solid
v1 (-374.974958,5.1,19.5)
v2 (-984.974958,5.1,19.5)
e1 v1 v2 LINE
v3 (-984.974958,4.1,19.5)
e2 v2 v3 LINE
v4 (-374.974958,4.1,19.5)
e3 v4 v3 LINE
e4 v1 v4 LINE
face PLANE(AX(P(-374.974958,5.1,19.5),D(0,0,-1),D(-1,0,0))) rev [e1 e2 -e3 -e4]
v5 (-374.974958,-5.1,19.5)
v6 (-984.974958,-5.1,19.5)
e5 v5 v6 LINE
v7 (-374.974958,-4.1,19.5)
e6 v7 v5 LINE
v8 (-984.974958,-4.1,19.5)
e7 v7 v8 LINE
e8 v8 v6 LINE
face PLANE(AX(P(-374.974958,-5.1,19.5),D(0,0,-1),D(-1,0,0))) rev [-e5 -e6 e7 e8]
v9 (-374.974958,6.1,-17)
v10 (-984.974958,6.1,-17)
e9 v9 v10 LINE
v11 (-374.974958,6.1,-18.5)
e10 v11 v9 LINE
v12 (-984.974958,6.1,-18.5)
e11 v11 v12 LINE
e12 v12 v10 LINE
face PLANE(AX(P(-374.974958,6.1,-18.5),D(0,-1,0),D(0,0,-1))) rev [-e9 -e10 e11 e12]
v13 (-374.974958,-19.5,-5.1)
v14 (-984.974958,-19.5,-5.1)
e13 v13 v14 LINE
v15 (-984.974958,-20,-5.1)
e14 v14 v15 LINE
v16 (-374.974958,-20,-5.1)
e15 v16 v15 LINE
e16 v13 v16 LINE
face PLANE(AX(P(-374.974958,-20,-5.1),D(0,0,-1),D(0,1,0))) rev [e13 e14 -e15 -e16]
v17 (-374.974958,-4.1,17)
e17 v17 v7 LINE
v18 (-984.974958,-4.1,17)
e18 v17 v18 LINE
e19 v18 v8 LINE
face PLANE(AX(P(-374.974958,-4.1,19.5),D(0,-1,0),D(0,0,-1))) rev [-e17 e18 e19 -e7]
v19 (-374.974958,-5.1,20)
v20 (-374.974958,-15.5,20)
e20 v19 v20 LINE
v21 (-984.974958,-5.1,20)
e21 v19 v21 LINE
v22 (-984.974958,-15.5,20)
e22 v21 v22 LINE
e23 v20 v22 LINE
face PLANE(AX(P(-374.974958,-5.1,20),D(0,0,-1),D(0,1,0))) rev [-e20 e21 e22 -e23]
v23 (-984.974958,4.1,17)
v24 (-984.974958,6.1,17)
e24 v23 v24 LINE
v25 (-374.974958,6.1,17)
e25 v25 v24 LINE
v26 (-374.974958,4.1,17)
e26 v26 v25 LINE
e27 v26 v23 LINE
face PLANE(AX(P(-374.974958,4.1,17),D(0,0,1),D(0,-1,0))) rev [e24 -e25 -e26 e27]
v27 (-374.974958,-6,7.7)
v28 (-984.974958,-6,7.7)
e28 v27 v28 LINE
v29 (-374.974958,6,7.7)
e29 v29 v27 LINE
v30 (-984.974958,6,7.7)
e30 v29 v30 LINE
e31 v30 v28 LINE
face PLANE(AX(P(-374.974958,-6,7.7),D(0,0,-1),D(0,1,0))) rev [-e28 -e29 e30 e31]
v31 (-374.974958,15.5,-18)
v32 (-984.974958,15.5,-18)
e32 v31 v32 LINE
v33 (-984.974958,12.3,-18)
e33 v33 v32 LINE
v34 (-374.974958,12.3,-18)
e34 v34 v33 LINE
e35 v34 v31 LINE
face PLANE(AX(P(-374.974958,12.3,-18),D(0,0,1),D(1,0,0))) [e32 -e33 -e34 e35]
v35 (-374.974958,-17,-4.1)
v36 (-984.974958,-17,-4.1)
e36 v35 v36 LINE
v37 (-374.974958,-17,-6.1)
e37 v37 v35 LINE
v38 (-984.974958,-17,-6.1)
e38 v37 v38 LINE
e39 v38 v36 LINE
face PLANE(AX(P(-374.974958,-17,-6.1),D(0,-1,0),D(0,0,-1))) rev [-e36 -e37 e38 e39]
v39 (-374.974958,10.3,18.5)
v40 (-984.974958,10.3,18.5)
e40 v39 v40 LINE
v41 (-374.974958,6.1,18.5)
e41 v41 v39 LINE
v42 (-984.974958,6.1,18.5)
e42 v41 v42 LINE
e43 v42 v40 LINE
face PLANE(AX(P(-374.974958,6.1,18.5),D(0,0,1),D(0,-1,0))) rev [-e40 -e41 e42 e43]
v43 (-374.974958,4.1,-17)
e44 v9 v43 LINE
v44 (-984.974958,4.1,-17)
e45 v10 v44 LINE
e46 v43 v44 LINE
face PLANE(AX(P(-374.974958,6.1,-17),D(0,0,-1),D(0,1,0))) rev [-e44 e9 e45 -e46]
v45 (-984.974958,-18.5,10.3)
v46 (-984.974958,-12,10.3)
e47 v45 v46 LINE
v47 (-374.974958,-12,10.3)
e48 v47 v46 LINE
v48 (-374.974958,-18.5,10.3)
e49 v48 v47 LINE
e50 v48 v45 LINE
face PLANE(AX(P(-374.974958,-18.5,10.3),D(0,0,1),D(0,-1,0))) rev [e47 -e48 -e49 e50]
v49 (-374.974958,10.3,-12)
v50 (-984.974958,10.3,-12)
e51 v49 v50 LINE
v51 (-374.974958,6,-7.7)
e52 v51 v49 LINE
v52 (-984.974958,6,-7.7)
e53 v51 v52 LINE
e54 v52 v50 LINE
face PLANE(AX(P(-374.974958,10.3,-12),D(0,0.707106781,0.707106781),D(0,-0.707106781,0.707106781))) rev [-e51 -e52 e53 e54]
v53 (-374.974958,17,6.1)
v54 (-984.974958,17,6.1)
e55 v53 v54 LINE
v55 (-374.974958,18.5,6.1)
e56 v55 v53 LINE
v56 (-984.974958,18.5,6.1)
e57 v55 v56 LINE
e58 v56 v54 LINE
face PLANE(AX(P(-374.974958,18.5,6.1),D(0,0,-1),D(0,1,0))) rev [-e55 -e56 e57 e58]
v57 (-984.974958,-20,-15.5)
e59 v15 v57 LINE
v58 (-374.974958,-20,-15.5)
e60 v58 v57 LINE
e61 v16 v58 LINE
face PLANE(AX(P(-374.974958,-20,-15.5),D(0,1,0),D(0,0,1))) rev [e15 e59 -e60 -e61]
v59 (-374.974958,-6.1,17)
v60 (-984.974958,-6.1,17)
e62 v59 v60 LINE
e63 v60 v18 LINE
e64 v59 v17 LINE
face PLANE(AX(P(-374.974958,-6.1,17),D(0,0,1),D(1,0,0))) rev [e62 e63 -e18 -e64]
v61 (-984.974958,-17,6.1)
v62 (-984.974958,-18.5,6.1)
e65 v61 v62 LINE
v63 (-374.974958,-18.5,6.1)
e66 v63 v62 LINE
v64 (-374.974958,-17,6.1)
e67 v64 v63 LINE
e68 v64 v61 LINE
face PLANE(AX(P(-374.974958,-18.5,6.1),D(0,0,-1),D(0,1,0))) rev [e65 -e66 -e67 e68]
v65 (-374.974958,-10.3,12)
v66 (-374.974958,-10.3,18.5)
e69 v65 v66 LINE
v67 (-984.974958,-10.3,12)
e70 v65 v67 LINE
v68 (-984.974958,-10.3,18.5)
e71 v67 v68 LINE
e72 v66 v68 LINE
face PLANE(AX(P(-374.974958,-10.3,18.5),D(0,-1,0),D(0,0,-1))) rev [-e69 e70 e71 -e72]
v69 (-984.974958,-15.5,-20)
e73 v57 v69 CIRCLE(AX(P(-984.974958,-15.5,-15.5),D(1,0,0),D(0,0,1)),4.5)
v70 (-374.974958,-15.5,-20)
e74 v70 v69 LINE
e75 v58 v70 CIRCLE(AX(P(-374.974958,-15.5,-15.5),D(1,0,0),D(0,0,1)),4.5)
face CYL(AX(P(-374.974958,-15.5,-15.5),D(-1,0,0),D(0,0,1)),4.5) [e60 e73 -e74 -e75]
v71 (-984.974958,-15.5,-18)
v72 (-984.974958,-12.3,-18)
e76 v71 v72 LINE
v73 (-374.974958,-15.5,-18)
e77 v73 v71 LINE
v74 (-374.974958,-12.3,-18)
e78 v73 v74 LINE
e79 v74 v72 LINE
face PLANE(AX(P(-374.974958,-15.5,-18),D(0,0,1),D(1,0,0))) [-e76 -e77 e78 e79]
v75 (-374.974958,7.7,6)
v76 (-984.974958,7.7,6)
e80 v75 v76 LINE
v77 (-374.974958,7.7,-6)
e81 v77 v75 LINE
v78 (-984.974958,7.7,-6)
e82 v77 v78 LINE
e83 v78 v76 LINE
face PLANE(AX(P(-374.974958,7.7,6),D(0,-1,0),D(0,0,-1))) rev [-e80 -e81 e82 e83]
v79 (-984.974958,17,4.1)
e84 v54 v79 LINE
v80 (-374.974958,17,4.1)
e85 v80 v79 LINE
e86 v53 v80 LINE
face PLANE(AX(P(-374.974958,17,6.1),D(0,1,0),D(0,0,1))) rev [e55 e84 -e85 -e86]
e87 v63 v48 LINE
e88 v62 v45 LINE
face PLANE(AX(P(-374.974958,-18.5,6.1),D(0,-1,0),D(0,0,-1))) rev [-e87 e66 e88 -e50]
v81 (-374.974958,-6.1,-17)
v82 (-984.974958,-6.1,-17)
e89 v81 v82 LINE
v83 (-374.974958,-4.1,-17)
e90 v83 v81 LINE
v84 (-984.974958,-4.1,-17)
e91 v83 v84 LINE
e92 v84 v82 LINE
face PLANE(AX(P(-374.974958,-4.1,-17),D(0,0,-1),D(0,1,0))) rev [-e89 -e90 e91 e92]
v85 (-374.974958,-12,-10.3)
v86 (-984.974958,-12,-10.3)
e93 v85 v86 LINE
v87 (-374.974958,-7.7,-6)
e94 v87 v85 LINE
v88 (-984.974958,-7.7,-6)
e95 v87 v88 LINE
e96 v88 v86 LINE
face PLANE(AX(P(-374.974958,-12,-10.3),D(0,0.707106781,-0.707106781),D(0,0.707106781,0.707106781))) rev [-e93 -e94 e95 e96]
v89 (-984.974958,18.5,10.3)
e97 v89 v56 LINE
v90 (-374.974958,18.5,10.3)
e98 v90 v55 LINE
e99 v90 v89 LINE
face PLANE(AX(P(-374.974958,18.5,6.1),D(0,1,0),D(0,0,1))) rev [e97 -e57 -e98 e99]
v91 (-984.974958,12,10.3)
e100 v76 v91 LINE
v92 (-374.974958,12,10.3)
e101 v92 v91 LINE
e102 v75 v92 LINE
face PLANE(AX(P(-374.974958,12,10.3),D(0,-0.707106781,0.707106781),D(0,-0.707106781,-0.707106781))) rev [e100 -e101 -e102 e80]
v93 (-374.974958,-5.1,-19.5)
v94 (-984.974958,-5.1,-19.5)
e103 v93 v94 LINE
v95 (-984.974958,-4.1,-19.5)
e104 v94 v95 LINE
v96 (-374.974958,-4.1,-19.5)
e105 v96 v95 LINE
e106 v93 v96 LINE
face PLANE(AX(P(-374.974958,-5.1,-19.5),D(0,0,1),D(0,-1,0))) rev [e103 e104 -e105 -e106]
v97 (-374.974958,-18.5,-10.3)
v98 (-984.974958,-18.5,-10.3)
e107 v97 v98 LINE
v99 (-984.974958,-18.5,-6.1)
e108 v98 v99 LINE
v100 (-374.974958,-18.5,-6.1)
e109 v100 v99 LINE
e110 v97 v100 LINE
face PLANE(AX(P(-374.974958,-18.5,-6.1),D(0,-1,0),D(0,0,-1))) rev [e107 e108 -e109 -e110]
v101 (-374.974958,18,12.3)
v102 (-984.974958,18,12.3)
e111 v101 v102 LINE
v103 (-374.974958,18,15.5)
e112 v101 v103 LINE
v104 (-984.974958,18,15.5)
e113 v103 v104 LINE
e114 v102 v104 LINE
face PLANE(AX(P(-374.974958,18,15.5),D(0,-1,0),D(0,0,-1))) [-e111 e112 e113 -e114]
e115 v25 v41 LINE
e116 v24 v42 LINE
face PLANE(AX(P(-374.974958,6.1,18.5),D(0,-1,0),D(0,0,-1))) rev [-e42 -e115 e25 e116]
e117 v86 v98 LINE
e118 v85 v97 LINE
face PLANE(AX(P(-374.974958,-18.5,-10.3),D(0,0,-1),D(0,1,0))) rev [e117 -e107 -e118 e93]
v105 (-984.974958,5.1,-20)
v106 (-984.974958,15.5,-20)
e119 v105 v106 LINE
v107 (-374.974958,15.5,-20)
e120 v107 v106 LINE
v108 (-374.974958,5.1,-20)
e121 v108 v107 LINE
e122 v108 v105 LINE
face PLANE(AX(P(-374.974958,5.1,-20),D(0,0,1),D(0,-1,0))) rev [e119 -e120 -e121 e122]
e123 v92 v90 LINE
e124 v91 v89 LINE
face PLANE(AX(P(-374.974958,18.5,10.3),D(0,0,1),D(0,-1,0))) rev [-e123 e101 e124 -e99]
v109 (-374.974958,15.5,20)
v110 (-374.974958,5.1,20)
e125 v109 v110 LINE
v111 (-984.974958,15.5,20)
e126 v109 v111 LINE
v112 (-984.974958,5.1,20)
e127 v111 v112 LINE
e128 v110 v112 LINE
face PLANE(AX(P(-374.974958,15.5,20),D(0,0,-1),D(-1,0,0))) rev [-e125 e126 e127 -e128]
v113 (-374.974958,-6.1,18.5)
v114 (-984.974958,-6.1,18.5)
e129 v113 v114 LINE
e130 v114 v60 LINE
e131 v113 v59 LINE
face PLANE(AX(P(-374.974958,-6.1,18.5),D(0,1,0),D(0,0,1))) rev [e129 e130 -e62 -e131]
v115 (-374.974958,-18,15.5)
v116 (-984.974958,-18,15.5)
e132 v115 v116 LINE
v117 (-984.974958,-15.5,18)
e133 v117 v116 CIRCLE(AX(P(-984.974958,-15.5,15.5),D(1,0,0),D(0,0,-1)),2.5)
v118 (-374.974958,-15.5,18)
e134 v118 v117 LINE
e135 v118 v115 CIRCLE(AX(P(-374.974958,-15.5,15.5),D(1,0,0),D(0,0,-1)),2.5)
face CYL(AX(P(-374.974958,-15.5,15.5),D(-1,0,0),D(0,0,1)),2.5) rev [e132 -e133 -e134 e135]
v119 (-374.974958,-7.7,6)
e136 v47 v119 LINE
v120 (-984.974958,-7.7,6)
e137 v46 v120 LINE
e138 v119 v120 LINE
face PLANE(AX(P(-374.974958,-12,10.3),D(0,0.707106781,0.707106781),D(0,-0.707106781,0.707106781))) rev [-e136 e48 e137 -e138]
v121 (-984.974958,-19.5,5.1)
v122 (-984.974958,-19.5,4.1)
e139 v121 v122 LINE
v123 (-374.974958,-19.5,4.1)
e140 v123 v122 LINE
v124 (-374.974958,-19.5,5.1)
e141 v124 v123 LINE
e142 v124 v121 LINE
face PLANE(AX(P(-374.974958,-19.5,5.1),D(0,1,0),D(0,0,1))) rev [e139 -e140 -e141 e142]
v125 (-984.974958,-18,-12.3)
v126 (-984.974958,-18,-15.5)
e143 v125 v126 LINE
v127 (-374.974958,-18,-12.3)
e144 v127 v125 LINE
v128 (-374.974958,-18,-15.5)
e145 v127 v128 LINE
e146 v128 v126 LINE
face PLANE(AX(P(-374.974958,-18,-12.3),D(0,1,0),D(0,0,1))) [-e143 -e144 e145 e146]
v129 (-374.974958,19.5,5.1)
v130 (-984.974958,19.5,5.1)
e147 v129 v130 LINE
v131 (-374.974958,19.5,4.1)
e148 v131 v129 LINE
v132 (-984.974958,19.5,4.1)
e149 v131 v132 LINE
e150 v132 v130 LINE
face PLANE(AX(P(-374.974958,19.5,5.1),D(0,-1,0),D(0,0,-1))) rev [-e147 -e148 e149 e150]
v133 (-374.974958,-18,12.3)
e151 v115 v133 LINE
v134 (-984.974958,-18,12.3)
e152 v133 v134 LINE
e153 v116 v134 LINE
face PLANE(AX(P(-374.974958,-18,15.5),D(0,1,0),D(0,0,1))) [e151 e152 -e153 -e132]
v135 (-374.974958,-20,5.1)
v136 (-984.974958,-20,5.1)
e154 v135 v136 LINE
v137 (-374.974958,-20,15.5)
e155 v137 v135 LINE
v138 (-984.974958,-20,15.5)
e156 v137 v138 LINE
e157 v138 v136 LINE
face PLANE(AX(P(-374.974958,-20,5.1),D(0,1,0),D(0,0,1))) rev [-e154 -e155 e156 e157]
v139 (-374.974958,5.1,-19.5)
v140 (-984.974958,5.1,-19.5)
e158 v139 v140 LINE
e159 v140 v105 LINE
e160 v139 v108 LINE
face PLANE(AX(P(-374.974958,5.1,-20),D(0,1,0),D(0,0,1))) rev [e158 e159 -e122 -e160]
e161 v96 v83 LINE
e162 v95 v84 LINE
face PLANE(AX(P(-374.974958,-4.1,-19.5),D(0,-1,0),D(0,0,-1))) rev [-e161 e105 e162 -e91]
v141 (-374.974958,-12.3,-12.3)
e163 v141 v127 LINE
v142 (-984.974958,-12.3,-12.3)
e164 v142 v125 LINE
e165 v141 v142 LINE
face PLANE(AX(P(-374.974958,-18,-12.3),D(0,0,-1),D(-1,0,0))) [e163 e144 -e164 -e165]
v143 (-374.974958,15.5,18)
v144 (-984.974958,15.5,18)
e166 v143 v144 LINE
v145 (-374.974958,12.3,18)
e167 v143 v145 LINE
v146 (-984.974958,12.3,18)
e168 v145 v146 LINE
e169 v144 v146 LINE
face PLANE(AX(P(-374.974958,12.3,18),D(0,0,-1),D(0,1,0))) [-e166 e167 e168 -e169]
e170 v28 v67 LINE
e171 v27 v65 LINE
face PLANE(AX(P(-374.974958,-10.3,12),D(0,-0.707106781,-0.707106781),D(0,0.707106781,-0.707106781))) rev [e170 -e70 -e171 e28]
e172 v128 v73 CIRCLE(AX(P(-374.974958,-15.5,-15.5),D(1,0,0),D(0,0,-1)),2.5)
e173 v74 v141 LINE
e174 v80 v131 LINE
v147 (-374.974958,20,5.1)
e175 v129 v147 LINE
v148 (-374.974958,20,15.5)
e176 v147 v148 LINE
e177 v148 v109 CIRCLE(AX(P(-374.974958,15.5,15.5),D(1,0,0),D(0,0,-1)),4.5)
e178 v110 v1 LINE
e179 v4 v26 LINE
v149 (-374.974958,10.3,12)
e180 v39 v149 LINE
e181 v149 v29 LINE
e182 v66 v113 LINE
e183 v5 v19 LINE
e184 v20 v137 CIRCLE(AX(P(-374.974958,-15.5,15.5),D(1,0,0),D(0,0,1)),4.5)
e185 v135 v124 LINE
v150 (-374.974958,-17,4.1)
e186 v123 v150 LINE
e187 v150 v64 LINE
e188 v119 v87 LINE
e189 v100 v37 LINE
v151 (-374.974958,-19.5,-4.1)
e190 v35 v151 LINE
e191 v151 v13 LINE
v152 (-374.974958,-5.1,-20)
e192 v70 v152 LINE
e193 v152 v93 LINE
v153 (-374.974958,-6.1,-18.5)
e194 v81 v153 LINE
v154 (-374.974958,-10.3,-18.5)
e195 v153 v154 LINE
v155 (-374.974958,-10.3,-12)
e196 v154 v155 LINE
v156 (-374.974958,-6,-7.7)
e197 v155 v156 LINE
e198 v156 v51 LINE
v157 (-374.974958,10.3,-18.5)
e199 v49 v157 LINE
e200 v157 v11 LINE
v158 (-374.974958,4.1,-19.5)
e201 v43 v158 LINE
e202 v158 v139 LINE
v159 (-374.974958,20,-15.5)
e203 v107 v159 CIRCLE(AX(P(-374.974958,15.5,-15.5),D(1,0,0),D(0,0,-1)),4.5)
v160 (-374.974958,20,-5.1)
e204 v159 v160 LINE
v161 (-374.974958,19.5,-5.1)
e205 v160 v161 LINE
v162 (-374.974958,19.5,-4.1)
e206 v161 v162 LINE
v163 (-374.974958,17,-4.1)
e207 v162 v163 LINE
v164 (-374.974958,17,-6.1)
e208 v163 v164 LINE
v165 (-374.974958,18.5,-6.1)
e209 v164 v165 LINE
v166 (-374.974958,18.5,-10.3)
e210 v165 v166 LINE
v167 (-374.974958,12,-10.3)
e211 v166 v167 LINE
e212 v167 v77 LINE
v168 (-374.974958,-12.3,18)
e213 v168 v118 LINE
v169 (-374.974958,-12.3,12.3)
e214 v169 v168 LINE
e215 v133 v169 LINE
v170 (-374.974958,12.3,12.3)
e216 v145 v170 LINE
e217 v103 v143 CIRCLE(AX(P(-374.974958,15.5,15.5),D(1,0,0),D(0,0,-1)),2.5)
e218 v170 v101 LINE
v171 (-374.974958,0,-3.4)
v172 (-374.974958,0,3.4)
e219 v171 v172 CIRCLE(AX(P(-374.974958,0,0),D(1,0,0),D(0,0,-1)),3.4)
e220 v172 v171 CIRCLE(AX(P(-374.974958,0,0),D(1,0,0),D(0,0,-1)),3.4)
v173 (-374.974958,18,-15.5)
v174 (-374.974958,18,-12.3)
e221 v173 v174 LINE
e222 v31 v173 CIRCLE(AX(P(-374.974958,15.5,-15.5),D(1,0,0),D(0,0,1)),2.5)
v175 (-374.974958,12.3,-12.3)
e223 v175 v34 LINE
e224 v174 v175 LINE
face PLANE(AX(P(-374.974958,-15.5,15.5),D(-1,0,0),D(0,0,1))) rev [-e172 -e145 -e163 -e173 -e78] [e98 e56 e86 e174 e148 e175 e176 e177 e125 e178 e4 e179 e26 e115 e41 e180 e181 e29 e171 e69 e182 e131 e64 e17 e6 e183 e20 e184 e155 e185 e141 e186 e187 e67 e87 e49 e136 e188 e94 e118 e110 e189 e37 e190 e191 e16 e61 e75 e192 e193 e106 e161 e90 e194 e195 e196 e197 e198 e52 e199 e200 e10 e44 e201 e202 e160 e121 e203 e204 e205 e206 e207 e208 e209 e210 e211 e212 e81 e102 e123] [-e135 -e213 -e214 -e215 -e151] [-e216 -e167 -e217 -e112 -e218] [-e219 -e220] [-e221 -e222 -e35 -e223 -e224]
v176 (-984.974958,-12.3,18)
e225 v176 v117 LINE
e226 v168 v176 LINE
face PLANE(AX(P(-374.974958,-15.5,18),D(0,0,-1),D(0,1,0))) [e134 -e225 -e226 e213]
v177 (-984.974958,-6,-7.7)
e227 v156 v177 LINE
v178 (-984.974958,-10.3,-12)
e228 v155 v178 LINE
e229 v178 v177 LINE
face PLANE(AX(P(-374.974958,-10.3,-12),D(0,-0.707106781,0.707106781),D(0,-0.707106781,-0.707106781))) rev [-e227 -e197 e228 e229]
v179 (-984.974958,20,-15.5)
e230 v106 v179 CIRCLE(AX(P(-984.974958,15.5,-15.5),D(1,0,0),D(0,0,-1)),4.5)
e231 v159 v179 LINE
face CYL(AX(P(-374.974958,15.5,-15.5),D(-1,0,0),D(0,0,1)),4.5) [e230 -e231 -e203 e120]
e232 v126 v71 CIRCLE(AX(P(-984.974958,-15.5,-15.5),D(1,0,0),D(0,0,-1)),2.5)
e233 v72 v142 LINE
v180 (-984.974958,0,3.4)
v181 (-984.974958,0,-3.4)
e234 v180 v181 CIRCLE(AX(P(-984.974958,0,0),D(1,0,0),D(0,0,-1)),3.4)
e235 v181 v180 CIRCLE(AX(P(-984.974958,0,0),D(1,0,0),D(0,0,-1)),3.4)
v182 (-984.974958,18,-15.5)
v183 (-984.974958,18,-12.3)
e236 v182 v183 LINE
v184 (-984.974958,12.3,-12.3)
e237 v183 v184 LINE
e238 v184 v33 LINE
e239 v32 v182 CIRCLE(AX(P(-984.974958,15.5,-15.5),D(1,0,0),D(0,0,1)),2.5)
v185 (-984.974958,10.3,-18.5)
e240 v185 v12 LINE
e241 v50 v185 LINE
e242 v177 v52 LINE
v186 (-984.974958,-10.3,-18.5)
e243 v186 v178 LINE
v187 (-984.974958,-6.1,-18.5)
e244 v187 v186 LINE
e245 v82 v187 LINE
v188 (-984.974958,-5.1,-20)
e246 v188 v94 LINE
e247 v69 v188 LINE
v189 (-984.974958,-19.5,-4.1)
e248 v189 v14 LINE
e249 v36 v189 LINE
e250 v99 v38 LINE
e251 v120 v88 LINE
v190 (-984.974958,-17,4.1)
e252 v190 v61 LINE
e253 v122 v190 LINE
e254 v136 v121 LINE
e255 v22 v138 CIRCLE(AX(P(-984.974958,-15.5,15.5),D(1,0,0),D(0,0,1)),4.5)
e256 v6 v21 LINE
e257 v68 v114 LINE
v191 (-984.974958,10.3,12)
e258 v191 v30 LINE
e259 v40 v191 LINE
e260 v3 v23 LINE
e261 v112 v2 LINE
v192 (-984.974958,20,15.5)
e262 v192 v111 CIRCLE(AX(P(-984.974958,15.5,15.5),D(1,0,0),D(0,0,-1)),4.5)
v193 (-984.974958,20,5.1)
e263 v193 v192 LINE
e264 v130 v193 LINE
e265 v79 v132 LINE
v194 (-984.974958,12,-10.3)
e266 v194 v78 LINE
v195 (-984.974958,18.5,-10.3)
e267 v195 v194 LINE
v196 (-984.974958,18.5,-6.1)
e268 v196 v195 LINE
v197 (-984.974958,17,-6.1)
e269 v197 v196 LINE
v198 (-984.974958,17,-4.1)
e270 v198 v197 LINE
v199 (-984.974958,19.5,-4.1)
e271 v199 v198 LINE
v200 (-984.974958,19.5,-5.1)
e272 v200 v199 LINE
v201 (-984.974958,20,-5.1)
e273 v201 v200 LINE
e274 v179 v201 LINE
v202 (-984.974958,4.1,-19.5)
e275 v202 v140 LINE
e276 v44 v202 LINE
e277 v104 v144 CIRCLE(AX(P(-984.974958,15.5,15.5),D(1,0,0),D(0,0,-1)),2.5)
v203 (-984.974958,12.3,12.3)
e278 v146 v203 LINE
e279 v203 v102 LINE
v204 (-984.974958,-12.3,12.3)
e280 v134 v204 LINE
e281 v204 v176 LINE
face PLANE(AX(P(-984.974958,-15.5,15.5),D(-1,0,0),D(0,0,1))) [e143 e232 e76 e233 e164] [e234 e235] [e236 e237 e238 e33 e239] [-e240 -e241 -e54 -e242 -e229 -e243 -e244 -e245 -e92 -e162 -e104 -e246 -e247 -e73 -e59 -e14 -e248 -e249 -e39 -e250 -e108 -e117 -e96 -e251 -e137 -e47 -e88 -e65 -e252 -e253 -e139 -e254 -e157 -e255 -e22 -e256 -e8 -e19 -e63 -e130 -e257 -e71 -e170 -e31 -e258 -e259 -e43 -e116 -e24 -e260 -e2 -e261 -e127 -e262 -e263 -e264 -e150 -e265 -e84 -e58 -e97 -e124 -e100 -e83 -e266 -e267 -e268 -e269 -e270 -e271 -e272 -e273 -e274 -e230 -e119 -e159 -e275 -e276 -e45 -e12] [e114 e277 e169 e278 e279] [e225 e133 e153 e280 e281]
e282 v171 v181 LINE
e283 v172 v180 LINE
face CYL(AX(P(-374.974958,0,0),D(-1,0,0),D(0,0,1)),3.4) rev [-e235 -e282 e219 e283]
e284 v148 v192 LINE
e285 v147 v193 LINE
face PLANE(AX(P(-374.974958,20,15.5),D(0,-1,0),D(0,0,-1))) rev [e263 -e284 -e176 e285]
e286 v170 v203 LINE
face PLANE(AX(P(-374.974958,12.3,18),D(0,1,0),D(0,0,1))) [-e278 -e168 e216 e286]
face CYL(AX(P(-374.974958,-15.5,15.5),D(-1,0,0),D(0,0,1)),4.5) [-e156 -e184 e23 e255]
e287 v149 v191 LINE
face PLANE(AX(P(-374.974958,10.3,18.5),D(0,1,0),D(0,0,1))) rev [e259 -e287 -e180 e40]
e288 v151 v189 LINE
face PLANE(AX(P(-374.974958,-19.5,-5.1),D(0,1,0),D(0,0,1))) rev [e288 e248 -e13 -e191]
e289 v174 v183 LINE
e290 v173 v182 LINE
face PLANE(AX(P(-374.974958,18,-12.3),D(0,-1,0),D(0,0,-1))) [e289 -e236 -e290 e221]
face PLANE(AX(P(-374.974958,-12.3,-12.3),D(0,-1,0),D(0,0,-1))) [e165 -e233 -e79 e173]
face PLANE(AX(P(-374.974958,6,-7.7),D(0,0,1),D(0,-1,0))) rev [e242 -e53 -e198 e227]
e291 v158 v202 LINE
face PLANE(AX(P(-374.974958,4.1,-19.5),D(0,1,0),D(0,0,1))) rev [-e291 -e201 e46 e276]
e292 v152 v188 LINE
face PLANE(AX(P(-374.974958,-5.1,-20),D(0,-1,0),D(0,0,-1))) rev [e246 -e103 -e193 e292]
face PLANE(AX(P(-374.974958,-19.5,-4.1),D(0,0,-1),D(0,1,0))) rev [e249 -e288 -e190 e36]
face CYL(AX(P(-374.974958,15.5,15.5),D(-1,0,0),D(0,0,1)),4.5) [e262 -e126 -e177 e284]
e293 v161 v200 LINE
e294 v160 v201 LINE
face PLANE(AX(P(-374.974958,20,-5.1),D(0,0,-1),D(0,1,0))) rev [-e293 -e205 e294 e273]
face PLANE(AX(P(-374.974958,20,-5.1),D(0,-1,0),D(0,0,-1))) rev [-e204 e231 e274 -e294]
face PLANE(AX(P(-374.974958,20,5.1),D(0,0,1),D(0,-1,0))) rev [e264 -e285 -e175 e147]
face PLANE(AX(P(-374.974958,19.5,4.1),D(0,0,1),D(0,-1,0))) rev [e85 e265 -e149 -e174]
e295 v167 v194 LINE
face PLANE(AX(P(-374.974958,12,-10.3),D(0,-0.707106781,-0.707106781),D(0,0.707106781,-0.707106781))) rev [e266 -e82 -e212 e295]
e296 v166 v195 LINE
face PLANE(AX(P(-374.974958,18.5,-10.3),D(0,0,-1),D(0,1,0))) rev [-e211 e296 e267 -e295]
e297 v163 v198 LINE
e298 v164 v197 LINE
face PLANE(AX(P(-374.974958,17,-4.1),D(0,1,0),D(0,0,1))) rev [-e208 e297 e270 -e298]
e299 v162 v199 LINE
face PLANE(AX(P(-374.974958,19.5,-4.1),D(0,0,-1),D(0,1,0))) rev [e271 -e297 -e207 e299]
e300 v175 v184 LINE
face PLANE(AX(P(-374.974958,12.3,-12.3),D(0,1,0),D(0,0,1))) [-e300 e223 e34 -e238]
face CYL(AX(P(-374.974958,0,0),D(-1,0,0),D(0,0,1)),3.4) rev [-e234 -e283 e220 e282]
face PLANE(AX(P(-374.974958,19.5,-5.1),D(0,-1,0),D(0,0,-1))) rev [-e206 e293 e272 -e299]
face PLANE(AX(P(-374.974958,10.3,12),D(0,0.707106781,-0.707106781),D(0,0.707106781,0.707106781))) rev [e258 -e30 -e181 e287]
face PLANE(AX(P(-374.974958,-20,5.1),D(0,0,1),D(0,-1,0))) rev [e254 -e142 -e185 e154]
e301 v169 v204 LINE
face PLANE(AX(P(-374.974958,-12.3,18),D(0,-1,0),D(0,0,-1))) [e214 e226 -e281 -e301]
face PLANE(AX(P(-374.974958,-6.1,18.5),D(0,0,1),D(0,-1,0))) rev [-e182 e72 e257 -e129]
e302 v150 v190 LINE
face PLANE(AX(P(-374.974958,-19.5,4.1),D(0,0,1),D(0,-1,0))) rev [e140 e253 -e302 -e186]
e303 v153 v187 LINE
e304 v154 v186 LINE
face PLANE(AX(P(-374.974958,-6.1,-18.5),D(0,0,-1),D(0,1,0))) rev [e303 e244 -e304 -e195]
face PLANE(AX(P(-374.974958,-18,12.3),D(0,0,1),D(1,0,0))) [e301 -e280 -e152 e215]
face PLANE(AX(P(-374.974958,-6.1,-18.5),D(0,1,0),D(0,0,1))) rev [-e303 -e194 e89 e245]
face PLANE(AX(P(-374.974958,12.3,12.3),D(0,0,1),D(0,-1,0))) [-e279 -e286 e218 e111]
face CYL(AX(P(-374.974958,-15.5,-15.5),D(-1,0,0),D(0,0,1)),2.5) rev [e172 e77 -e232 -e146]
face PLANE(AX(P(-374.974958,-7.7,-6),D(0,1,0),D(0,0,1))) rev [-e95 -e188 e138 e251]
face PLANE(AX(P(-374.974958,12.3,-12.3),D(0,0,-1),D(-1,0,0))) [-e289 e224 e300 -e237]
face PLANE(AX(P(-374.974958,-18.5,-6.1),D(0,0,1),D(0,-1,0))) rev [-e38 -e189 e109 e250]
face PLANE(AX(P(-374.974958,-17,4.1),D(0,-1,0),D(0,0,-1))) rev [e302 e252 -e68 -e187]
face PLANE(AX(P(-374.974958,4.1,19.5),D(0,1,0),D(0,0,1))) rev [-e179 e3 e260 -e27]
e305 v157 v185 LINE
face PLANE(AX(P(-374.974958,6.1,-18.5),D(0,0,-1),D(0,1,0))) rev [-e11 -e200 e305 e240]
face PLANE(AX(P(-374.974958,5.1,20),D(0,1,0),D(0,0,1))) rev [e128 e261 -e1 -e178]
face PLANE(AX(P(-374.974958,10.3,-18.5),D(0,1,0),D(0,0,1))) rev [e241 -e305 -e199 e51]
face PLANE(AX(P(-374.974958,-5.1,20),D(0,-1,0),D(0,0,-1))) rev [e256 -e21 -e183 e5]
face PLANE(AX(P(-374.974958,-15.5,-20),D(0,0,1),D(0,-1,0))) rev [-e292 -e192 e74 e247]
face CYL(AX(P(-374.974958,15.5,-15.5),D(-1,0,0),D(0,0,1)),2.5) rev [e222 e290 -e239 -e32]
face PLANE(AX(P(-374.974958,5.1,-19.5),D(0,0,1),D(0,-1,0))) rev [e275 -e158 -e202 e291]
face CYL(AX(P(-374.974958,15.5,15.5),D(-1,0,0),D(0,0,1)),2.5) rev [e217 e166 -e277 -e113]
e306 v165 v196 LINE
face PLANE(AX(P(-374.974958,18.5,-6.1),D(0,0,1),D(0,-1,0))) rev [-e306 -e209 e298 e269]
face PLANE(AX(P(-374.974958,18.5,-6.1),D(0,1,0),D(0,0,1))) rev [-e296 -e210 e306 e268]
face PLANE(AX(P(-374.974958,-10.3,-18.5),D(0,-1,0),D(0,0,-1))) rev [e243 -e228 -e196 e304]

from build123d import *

# Parameters (mm, degrees)
SKETCH1_R                                 = 3.4
ALUMINIUM_PROFILE_40_X_40B_X_R4_5_1_DEPTH = 610


with BuildPart() as part:
    # Sketch1 → Aluminium profile 40 X 40B X R4.5(1) (new body)
    with BuildSketch(Plane.YZ.offset(-984.974958264)):
        with BuildLine():
            Line((-5.1, 20), (-5.1, 19.5))
            Line((-5.1, 19.5), (-4.1, 19.5))
            Line((-4.1, 19.5), (-4.1, 17))
            Line((-4.1, 17), (-6.1, 17))
            Line((-6.1, 17), (-6.1, 18.5))
            Line((-6.1, 18.5), (-10.3, 18.5))
            Line((-10.3, 18.5), (-10.3, 12))
            Line((-10.3, 12), (-6, 7.7))
            Line((-6, 7.7), (6, 7.7))
            Line((6, 7.7), (10.3, 12))
            Line((10.3, 12), (10.3, 18.5))
            Line((10.3, 18.5), (6.1, 18.5))
            Line((6.1, 18.5), (6.1, 17))
            Line((6.1, 17), (4.1, 17))
            Line((4.1, 17), (4.1, 19.5))
            Line((4.1, 19.5), (5.1, 19.5))
            Line((5.1, 19.5), (5.1, 20))
            Line((5.1, 20), (15.5, 20))
            ThreePointArc((15.5, 20), (18.681980515, 18.681980515), (20, 15.5))
            Line((20, 15.5), (20, 5.1))
            Line((20, 5.1), (19.5, 5.1))
            Line((19.5, 5.1), (19.5, 4.1))
            Line((19.5, 4.1), (17, 4.1))
            Line((17, 4.1), (17, 6.1))
            Line((17, 6.1), (18.5, 6.1))
            Line((18.5, 6.1), (18.5, 10.3))
            Line((18.5, 10.3), (12, 10.3))
            Line((12, 10.3), (7.7, 6))
            Line((7.7, 6), (7.7, -6))
            Line((7.7, -6), (12, -10.3))
            Line((12, -10.3), (18.5, -10.3))
            Line((18.5, -10.3), (18.5, -6.1))
            Line((18.5, -6.1), (17, -6.1))
            Line((17, -6.1), (17, -4.1))
            Line((17, -4.1), (19.5, -4.1))
            Line((19.5, -4.1), (19.5, -5.1))
            Line((19.5, -5.1), (20, -5.1))
            Line((20, -5.1), (20, -15.5))
            ThreePointArc((20, -15.5), (18.681980515, -18.681980515), (15.5, -20))
            Line((15.5, -20), (5.1, -20))
            Line((5.1, -20), (5.1, -19.5))
            Line((5.1, -19.5), (4.1, -19.5))
            Line((4.1, -19.5), (4.1, -17))
            Line((4.1, -17), (6.1, -17))
            Line((6.1, -17), (6.1, -18.5))
            Line((6.1, -18.5), (10.3, -18.5))
            Line((10.3, -18.5), (10.3, -12))
            Line((10.3, -12), (6, -7.7))
            Line((6, -7.7), (-6, -7.7))
            Line((-6, -7.7), (-10.3, -12))
            Line((-10.3, -12), (-10.3, -18.5))
            Line((-10.3, -18.5), (-6.1, -18.5))
            Line((-6.1, -18.5), (-6.1, -17))
            Line((-6.1, -17), (-4.1, -17))
            Line((-4.1, -17), (-4.1, -19.5))
            Line((-4.1, -19.5), (-5.1, -19.5))
            Line((-5.1, -19.5), (-5.1, -20))
            Line((-5.1, -20), (-15.5, -20))
            ThreePointArc((-15.5, -20), (-18.681980515, -18.681980515), (-20, -15.5))
            Line((-20, -15.5), (-20, -5.1))
            Line((-20, -5.1), (-19.5, -5.1))
            Line((-19.5, -5.1), (-19.5, -4.1))
            Line((-19.5, -4.1), (-17, -4.1))
            Line((-17, -4.1), (-17, -6.1))
            Line((-17, -6.1), (-18.5, -6.1))
            Line((-18.5, -6.1), (-18.5, -10.3))
            Line((-18.5, -10.3), (-12, -10.3))
            Line((-12, -10.3), (-7.7, -6))
            Line((-7.7, -6), (-7.7, 6))
            Line((-7.7, 6), (-12, 10.3))
            Line((-12, 10.3), (-18.5, 10.3))
            Line((-18.5, 10.3), (-18.5, 6.1))
            Line((-18.5, 6.1), (-17, 6.1))
            Line((-17, 6.1), (-17, 4.1))
            Line((-17, 4.1), (-19.5, 4.1))
            Line((-19.5, 4.1), (-19.5, 5.1))
            Line((-19.5, 5.1), (-20, 5.1))
            Line((-20, 5.1), (-20, 15.5))
            ThreePointArc((-20, 15.5), (-18.681980515, 18.681980515), (-15.5, 20))
            Line((-15.5, 20), (-5.1, 20))
        make_face()
        Circle(SKETCH1_R, mode=Mode.SUBTRACT)
        with BuildLine():
            Line((12.3, 18), (15.5, 18))
            ThreePointArc((15.5, 18), (17.267766953, 17.267766953), (18, 15.5))
            Line((18, 15.5), (18, 12.3))
            Line((18, 12.3), (12.3, 12.3))
            Line((12.3, 12.3), (12.3, 18))
        make_face(mode=Mode.SUBTRACT)
        with BuildLine():
            Line((-15.5, 18), (-12.3, 18))
            Line((-12.3, 18), (-12.3, 12.3))
            Line((-12.3, 12.3), (-18, 12.3))
            Line((-18, 12.3), (-18, 15.5))
            ThreePointArc((-18, 15.5), (-17.267766953, 17.267766953), (-15.5, 18))
        make_face(mode=Mode.SUBTRACT)
        with BuildLine():
            Line((-18, -12.3), (-12.3, -12.3))
            Line((-12.3, -12.3), (-12.3, -18))
            Line((-12.3, -18), (-15.5, -18))
            ThreePointArc((-15.5, -18), (-17.267766953, -17.267766953), (-18, -15.5))
            Line((-18, -15.5), (-18, -12.3))
        make_face(mode=Mode.SUBTRACT)
        with BuildLine():
            Line((12.3, -12.3), (18, -12.3))
            Line((18, -12.3), (18, -15.5))
            ThreePointArc((18, -15.5), (17.267766953, -17.267766953), (15.5, -18))
            Line((15.5, -18), (12.3, -18))
            Line((12.3, -18), (12.3, -12.3))
        make_face(mode=Mode.SUBTRACT)
    extrude(amount=ALUMINIUM_PROFILE_40_X_40B_X_R4_5_1_DEPTH)


solid = part.part
